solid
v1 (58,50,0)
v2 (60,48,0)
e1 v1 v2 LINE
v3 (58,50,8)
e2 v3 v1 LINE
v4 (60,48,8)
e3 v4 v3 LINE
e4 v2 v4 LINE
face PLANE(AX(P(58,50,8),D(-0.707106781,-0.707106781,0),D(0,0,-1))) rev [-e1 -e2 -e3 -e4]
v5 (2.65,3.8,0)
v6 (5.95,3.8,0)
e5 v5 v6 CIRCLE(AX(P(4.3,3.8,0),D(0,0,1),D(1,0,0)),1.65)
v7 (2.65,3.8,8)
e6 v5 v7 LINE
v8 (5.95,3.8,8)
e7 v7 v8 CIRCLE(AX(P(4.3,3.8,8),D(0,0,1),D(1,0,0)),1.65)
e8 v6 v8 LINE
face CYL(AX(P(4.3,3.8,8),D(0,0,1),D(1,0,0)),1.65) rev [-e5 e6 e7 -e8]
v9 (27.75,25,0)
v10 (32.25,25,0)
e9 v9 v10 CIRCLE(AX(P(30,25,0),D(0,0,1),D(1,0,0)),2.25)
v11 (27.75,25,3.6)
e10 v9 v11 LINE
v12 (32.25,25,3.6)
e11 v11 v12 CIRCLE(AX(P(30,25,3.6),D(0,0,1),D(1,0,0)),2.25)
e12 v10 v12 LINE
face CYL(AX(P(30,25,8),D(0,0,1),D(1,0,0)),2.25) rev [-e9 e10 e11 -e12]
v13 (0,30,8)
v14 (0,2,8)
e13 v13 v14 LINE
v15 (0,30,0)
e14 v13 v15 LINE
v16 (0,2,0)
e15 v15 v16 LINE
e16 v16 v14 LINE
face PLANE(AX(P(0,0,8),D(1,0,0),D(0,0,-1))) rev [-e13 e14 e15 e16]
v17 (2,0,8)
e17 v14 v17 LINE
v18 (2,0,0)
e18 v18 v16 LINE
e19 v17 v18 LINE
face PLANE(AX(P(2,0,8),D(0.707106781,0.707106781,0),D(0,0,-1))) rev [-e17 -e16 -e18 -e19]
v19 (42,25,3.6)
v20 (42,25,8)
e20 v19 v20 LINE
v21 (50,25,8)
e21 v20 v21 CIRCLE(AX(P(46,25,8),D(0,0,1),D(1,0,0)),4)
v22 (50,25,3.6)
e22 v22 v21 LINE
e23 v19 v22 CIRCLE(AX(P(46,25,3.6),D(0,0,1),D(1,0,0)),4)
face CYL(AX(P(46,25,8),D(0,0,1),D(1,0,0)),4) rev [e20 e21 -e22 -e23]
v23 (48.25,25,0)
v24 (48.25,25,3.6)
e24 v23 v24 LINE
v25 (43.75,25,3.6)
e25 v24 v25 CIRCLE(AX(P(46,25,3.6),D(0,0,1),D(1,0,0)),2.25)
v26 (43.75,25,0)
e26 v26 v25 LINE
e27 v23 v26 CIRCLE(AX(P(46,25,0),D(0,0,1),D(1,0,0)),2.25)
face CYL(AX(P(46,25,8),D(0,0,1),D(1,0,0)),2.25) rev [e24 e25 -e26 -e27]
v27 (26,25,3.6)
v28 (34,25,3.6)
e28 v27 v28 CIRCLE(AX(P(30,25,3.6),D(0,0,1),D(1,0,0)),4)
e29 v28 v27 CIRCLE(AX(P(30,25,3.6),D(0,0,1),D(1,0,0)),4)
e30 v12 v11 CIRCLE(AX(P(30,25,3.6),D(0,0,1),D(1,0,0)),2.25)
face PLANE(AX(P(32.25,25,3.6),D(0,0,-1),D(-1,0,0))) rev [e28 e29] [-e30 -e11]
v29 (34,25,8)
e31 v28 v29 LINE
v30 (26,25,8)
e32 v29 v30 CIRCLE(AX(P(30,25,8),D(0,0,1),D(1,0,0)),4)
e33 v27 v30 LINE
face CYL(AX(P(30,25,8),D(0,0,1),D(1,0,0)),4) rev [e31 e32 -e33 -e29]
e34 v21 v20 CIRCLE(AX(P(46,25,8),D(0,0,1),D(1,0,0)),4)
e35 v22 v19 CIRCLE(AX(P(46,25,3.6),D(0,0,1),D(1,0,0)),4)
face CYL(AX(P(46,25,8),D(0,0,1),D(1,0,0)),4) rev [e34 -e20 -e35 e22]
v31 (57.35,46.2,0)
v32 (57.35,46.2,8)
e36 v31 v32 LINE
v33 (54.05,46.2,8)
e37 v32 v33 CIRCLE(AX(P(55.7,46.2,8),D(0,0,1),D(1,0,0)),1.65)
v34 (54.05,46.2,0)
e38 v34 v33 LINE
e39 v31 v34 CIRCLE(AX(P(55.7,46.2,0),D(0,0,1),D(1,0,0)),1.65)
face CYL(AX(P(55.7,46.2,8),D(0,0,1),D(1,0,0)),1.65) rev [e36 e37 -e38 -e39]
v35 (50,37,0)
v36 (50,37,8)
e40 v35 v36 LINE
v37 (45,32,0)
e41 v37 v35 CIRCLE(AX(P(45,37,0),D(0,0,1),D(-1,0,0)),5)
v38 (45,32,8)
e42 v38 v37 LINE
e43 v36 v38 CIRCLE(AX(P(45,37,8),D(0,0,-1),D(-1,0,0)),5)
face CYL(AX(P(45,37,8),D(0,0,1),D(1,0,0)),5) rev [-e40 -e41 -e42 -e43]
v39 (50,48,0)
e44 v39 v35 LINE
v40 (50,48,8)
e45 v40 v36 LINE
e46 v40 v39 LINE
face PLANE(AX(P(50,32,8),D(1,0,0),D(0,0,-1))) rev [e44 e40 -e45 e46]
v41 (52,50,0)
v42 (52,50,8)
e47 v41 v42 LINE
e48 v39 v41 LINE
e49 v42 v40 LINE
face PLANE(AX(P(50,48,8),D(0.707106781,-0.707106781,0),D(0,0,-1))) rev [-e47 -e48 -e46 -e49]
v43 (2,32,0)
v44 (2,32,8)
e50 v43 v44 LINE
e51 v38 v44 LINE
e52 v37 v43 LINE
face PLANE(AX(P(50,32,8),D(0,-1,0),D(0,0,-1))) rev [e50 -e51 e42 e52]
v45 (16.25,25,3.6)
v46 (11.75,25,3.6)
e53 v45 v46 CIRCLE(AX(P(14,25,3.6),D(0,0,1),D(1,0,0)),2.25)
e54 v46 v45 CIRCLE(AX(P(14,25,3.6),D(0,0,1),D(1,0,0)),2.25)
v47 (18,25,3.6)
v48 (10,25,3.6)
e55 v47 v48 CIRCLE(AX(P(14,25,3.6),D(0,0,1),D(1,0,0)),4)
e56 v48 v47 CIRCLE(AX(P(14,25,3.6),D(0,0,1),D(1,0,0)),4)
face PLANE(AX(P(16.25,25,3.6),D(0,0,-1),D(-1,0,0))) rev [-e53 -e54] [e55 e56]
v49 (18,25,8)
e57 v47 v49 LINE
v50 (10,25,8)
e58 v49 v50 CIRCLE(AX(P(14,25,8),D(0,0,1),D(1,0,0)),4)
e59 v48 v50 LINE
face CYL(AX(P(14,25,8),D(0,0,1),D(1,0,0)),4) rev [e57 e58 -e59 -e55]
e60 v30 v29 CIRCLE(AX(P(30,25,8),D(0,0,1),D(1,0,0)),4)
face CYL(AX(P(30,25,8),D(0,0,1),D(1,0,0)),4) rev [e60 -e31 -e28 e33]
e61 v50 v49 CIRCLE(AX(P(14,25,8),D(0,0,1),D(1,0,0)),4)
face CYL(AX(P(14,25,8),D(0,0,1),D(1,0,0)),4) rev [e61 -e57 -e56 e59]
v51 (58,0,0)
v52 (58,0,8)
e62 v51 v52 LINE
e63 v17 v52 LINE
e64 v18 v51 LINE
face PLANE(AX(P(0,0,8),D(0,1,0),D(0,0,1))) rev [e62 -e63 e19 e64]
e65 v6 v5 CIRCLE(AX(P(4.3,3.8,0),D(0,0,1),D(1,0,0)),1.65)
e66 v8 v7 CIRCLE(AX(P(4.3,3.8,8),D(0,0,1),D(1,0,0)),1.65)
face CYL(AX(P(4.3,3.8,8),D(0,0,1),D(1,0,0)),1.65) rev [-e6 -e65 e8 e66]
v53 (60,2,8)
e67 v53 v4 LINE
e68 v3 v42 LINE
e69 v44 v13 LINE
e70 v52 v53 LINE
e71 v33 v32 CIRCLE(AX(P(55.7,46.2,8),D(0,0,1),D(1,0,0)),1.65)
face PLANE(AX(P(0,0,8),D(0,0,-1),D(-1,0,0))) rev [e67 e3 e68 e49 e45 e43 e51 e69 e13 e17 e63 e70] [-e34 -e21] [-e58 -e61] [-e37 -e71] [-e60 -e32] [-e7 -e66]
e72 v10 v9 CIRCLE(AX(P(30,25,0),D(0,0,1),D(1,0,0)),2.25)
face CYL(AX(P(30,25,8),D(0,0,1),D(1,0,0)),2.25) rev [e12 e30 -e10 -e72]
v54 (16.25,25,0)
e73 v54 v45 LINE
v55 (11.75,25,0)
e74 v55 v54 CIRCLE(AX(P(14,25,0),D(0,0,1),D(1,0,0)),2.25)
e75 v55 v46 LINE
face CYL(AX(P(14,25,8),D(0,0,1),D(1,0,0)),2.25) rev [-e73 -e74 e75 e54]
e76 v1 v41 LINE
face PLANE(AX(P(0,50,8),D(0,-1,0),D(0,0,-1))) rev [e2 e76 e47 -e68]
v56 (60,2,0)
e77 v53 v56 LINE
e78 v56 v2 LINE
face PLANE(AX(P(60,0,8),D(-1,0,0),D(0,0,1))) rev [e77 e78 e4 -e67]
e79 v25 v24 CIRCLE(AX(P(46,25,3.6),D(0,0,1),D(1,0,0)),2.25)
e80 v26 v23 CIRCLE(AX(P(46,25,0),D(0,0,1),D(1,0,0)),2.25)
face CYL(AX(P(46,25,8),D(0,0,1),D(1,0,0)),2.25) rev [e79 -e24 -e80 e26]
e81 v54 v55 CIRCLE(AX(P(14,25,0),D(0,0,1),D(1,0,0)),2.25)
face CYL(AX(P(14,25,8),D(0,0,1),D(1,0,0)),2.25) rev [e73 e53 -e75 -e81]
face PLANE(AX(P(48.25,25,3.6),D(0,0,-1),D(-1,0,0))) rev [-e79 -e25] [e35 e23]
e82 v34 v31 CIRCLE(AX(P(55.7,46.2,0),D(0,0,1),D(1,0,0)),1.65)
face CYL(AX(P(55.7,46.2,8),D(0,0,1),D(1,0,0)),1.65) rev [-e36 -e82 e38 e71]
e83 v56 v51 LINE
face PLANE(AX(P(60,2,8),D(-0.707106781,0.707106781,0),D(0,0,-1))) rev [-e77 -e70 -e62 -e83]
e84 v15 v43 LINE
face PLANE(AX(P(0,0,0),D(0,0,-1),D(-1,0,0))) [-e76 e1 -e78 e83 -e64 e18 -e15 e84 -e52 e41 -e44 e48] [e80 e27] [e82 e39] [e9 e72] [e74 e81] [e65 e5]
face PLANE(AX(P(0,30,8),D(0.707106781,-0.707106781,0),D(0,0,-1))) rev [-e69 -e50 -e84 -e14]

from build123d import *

# Parameters (mm, degrees)
SKETCH1_W                                           = 60
SKETCH1_H                                           = 50
BOSS_EXTRUDE1_DEPTH                                 = 8
CBORE_FOR_M4_HEX_SOCKET_HEAD_CAP_SCREW1_D           = 4.5
CBORE_FOR_M4_HEX_SOCKET_HEAD_CAP_SCREW1_CBORE_D     = 8
CBORE_FOR_M4_HEX_SOCKET_HEAD_CAP_SCREW1_CBORE_DEPTH = 4.4
M4_TAPPED_HOLE1_D                                   = 3.3
CHAMFER1_SIZE                                       = 2
SKETCH6_W                                           = 50
SKETCH6_H                                           = 18
CUT_EXTRUDE1_DEPTH                                  = 79.511145706
CHAMFER2_SIZE                                       = 2
FILLET1_R                                           = 5


with BuildPart() as part:
    # Sketch1 → Boss-Extrude1 (new body)
    with BuildSketch(Plane.XY):
        with Locations((30, 25)):
            Rectangle(SKETCH1_W, SKETCH1_H)
    extrude(amount=BOSS_EXTRUDE1_DEPTH)

    # CBORE for M4 Hex Socket Head Cap Screw1 (through all)
    with Locations(Plane.XY.offset(8)):
        with Locations((46, 25), (30, 25), (14, 25)):
            CounterBoreHole(CBORE_FOR_M4_HEX_SOCKET_HEAD_CAP_SCREW1_D / 2, CBORE_FOR_M4_HEX_SOCKET_HEAD_CAP_SCREW1_CBORE_D / 2, CBORE_FOR_M4_HEX_SOCKET_HEAD_CAP_SCREW1_CBORE_DEPTH)

    # M4 Tapped Hole1 (through all)
    with Locations(Plane.XY.offset(8)):
        with Locations((55.7, 46.2), (4.3, 3.8)):
            Hole(M4_TAPPED_HOLE1_D / 2)

    # Chamfer1
    chamfer1_edges = [part.edges().sort_by_distance(p)[0] for p in [
        (0, 50, 4),
        (60, 50, 4),
        (60, 0, 4),
        (0, 0, 4),
    ]]
    chamfer(chamfer1_edges, length=CHAMFER1_SIZE)

    # Sketch6 → Cut-Extrude1 (cut, through all)
    with BuildSketch(Plane(origin=(0, 0, 0), x_dir=(-1, 0, 0), z_dir=(0, 0, -1))):
        with Locations((-25, 41)):
            Rectangle(SKETCH6_W, SKETCH6_H)
    extrude(amount=-CUT_EXTRUDE1_DEPTH, mode=Mode.SUBTRACT)

    # Chamfer2
    chamfer2_edges = [part.edges().sort_by_distance(p)[0] for p in [
        (50, 50, 4),
        (0, 32, 4),
    ]]
    chamfer(chamfer2_edges, length=CHAMFER2_SIZE)

    # Fillet1
    fillet1_edges = [part.edges().sort_by_distance(p)[0] for p in [
        (50, 32, 4),
    ]]
    fillet(fillet1_edges, radius=FILLET1_R)


solid = part.part
